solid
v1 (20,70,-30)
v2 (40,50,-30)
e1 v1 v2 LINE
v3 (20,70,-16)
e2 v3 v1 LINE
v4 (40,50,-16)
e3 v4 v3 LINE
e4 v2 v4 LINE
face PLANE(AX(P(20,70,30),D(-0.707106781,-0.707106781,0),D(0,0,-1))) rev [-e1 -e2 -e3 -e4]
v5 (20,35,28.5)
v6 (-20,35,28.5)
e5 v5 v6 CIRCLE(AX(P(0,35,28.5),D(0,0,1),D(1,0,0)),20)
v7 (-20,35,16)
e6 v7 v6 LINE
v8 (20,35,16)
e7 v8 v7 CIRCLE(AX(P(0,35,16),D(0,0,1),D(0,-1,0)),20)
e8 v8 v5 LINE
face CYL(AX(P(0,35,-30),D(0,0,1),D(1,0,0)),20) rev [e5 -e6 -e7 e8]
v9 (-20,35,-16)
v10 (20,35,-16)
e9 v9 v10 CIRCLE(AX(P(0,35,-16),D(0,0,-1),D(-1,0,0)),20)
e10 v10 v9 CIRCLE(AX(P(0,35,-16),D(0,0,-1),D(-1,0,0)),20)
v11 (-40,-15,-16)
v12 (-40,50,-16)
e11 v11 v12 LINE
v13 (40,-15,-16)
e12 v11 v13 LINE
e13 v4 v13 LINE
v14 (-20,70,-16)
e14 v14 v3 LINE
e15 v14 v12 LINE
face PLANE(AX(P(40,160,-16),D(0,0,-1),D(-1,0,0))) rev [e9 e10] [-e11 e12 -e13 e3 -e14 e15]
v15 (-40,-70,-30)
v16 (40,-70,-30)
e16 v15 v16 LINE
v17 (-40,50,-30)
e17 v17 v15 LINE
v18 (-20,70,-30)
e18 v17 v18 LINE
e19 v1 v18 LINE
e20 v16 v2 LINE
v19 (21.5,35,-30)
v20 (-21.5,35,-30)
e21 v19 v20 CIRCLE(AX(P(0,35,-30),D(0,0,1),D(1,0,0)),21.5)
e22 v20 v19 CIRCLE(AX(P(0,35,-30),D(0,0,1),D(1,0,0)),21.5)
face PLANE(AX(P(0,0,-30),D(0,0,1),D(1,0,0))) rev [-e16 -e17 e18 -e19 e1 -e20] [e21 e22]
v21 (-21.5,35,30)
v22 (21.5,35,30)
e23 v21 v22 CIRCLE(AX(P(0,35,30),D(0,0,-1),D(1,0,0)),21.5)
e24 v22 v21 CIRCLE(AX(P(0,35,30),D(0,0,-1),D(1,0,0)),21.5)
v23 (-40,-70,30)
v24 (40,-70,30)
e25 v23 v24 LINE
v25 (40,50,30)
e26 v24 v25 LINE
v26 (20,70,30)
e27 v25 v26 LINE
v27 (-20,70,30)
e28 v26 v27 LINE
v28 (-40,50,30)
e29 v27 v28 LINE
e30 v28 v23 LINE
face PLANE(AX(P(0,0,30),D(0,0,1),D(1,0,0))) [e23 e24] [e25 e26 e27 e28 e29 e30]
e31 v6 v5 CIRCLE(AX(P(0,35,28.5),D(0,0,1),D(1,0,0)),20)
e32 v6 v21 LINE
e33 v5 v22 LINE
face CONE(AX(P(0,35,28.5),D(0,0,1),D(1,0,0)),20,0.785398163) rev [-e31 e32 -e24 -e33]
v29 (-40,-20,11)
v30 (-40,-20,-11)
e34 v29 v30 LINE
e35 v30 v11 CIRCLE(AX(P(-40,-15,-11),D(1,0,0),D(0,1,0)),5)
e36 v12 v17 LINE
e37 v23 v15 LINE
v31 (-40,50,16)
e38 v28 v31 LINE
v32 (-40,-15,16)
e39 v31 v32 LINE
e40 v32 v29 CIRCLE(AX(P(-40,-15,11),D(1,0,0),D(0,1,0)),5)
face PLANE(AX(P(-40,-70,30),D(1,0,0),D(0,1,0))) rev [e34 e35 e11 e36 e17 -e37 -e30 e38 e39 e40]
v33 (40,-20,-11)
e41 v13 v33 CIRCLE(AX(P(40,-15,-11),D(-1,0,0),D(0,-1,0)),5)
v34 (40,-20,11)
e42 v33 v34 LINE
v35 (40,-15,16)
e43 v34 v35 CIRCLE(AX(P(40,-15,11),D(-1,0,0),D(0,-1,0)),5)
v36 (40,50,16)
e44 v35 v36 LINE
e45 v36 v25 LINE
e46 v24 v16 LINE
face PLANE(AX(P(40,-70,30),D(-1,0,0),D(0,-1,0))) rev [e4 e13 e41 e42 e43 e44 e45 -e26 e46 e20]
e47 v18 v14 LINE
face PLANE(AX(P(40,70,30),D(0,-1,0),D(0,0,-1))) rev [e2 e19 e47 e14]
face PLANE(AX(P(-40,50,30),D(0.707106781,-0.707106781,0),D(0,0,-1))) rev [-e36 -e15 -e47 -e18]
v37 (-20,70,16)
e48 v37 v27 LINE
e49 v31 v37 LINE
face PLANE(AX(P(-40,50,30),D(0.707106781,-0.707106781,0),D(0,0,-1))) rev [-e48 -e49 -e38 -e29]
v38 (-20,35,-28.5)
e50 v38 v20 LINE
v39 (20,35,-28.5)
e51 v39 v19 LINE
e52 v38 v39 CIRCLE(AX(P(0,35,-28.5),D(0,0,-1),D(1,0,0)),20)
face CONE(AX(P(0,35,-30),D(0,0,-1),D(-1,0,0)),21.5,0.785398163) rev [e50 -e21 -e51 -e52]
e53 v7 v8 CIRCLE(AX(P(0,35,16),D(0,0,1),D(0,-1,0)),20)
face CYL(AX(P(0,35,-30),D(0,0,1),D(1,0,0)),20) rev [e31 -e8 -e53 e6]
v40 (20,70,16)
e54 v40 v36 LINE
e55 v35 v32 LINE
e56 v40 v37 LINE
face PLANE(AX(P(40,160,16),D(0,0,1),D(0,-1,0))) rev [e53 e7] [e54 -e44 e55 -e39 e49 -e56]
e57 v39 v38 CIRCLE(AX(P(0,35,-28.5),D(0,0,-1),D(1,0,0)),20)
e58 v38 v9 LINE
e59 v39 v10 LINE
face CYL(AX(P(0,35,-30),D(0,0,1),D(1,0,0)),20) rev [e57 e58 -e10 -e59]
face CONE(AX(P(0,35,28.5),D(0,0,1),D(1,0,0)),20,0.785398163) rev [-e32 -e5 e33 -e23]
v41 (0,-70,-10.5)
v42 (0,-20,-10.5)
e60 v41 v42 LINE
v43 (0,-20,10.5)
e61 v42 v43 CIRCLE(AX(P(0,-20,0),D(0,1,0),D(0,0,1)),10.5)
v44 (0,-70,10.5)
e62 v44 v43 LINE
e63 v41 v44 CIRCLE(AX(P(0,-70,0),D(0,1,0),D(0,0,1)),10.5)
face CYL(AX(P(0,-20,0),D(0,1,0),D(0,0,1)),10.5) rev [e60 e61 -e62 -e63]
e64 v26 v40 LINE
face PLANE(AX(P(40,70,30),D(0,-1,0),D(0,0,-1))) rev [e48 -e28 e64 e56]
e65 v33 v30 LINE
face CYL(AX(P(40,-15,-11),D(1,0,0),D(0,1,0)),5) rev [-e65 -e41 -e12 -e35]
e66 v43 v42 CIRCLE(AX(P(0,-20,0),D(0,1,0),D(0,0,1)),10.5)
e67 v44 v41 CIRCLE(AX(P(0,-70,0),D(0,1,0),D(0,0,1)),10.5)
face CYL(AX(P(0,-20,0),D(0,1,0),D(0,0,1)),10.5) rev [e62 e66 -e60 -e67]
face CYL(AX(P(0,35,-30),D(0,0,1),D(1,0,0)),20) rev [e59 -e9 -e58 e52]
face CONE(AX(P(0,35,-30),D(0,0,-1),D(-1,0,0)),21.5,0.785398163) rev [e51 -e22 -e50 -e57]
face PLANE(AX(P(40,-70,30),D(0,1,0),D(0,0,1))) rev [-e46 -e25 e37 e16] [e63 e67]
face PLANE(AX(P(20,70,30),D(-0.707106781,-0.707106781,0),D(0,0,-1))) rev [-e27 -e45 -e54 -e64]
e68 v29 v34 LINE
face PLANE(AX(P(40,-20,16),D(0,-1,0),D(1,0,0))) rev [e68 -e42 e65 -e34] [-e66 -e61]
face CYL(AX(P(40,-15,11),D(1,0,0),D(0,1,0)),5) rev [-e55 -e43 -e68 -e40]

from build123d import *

# Parameters (mm, degrees)
SKETCH2_W               = 80
SKETCH2_H               = 140
BOSS_EXTRUDE1_DEPTH     = 30
CHAMFER1_SIZE           = 20
CUT_EXTRUDE1_DEPTH      = 111.453610172
CUT_EXTRUDE1_DEPTH_BACK = 111.453610172
SKETCH3_W               = 32
SKETCH3_H               = 180
FILLET1_R               = 5
CUT_EXTRUDE2_DEPTH      = 101.498756211
CUT_EXTRUDE2_DEPTH_BACK = 101.498756211
SKETCH4_R               = 20
CHAMFER2_SIZE           = 1.5
M24_TAPPED_HOLE1_D      = 21


with BuildPart() as part:
    # Sketch2 → Boss-Extrude1 (new, symmetric)
    with BuildSketch(Plane.XY):
        Rectangle(SKETCH2_W, SKETCH2_H)
    extrude(amount=BOSS_EXTRUDE1_DEPTH, both=True)

    # Chamfer1
    chamfer1_edges = [part.edges().sort_by_distance(p)[0] for p in [
        (-40, 70, 0),
        (40, 70, 0),
    ]]
    chamfer(chamfer1_edges, length=CHAMFER1_SIZE)

    # Sketch3 → Cut-Extrude1 (cut, two sides: drawn at the far end of the back side and taken through both)
    with BuildSketch(Plane.ZY.offset(40).offset(-CUT_EXTRUDE1_DEPTH_BACK)):
        with Locations((0, 70)):
            Rectangle(SKETCH3_W, SKETCH3_H)
    extrude(amount=CUT_EXTRUDE1_DEPTH + CUT_EXTRUDE1_DEPTH_BACK, mode=Mode.SUBTRACT)

    # Fillet1
    fillet1_edges = [part.edges().sort_by_distance(p)[0] for p in [
        (0, -20, 16),
        (0, -20, -16),
    ]]
    fillet(fillet1_edges, radius=FILLET1_R)

    # Sketch4 → Cut-Extrude2 (cut, two sides: drawn at the far end of the back side and taken through both)
    with BuildSketch(Plane.XY.offset(30).offset(-CUT_EXTRUDE2_DEPTH_BACK)):
        with Locations((0, 35)):
            Circle(SKETCH4_R)
    extrude(amount=CUT_EXTRUDE2_DEPTH + CUT_EXTRUDE2_DEPTH_BACK, mode=Mode.SUBTRACT)

    # Chamfer2
    chamfer2_edges = [part.edges().sort_by_distance(p)[0] for p in [
        (-20, 35, 30),
        (-20, 35, -30),
    ]]
    chamfer(chamfer2_edges, length=CHAMFER2_SIZE)

    # M24 Tapped Hole1 (through all)
    with Locations(Plane(origin=(0, -20, 0), x_dir=(1, 0, 0), z_dir=(0, 1, 0))):
        with Locations((0, 0)):
            Hole(M24_TAPPED_HOLE1_D / 2)


solid = part.part
